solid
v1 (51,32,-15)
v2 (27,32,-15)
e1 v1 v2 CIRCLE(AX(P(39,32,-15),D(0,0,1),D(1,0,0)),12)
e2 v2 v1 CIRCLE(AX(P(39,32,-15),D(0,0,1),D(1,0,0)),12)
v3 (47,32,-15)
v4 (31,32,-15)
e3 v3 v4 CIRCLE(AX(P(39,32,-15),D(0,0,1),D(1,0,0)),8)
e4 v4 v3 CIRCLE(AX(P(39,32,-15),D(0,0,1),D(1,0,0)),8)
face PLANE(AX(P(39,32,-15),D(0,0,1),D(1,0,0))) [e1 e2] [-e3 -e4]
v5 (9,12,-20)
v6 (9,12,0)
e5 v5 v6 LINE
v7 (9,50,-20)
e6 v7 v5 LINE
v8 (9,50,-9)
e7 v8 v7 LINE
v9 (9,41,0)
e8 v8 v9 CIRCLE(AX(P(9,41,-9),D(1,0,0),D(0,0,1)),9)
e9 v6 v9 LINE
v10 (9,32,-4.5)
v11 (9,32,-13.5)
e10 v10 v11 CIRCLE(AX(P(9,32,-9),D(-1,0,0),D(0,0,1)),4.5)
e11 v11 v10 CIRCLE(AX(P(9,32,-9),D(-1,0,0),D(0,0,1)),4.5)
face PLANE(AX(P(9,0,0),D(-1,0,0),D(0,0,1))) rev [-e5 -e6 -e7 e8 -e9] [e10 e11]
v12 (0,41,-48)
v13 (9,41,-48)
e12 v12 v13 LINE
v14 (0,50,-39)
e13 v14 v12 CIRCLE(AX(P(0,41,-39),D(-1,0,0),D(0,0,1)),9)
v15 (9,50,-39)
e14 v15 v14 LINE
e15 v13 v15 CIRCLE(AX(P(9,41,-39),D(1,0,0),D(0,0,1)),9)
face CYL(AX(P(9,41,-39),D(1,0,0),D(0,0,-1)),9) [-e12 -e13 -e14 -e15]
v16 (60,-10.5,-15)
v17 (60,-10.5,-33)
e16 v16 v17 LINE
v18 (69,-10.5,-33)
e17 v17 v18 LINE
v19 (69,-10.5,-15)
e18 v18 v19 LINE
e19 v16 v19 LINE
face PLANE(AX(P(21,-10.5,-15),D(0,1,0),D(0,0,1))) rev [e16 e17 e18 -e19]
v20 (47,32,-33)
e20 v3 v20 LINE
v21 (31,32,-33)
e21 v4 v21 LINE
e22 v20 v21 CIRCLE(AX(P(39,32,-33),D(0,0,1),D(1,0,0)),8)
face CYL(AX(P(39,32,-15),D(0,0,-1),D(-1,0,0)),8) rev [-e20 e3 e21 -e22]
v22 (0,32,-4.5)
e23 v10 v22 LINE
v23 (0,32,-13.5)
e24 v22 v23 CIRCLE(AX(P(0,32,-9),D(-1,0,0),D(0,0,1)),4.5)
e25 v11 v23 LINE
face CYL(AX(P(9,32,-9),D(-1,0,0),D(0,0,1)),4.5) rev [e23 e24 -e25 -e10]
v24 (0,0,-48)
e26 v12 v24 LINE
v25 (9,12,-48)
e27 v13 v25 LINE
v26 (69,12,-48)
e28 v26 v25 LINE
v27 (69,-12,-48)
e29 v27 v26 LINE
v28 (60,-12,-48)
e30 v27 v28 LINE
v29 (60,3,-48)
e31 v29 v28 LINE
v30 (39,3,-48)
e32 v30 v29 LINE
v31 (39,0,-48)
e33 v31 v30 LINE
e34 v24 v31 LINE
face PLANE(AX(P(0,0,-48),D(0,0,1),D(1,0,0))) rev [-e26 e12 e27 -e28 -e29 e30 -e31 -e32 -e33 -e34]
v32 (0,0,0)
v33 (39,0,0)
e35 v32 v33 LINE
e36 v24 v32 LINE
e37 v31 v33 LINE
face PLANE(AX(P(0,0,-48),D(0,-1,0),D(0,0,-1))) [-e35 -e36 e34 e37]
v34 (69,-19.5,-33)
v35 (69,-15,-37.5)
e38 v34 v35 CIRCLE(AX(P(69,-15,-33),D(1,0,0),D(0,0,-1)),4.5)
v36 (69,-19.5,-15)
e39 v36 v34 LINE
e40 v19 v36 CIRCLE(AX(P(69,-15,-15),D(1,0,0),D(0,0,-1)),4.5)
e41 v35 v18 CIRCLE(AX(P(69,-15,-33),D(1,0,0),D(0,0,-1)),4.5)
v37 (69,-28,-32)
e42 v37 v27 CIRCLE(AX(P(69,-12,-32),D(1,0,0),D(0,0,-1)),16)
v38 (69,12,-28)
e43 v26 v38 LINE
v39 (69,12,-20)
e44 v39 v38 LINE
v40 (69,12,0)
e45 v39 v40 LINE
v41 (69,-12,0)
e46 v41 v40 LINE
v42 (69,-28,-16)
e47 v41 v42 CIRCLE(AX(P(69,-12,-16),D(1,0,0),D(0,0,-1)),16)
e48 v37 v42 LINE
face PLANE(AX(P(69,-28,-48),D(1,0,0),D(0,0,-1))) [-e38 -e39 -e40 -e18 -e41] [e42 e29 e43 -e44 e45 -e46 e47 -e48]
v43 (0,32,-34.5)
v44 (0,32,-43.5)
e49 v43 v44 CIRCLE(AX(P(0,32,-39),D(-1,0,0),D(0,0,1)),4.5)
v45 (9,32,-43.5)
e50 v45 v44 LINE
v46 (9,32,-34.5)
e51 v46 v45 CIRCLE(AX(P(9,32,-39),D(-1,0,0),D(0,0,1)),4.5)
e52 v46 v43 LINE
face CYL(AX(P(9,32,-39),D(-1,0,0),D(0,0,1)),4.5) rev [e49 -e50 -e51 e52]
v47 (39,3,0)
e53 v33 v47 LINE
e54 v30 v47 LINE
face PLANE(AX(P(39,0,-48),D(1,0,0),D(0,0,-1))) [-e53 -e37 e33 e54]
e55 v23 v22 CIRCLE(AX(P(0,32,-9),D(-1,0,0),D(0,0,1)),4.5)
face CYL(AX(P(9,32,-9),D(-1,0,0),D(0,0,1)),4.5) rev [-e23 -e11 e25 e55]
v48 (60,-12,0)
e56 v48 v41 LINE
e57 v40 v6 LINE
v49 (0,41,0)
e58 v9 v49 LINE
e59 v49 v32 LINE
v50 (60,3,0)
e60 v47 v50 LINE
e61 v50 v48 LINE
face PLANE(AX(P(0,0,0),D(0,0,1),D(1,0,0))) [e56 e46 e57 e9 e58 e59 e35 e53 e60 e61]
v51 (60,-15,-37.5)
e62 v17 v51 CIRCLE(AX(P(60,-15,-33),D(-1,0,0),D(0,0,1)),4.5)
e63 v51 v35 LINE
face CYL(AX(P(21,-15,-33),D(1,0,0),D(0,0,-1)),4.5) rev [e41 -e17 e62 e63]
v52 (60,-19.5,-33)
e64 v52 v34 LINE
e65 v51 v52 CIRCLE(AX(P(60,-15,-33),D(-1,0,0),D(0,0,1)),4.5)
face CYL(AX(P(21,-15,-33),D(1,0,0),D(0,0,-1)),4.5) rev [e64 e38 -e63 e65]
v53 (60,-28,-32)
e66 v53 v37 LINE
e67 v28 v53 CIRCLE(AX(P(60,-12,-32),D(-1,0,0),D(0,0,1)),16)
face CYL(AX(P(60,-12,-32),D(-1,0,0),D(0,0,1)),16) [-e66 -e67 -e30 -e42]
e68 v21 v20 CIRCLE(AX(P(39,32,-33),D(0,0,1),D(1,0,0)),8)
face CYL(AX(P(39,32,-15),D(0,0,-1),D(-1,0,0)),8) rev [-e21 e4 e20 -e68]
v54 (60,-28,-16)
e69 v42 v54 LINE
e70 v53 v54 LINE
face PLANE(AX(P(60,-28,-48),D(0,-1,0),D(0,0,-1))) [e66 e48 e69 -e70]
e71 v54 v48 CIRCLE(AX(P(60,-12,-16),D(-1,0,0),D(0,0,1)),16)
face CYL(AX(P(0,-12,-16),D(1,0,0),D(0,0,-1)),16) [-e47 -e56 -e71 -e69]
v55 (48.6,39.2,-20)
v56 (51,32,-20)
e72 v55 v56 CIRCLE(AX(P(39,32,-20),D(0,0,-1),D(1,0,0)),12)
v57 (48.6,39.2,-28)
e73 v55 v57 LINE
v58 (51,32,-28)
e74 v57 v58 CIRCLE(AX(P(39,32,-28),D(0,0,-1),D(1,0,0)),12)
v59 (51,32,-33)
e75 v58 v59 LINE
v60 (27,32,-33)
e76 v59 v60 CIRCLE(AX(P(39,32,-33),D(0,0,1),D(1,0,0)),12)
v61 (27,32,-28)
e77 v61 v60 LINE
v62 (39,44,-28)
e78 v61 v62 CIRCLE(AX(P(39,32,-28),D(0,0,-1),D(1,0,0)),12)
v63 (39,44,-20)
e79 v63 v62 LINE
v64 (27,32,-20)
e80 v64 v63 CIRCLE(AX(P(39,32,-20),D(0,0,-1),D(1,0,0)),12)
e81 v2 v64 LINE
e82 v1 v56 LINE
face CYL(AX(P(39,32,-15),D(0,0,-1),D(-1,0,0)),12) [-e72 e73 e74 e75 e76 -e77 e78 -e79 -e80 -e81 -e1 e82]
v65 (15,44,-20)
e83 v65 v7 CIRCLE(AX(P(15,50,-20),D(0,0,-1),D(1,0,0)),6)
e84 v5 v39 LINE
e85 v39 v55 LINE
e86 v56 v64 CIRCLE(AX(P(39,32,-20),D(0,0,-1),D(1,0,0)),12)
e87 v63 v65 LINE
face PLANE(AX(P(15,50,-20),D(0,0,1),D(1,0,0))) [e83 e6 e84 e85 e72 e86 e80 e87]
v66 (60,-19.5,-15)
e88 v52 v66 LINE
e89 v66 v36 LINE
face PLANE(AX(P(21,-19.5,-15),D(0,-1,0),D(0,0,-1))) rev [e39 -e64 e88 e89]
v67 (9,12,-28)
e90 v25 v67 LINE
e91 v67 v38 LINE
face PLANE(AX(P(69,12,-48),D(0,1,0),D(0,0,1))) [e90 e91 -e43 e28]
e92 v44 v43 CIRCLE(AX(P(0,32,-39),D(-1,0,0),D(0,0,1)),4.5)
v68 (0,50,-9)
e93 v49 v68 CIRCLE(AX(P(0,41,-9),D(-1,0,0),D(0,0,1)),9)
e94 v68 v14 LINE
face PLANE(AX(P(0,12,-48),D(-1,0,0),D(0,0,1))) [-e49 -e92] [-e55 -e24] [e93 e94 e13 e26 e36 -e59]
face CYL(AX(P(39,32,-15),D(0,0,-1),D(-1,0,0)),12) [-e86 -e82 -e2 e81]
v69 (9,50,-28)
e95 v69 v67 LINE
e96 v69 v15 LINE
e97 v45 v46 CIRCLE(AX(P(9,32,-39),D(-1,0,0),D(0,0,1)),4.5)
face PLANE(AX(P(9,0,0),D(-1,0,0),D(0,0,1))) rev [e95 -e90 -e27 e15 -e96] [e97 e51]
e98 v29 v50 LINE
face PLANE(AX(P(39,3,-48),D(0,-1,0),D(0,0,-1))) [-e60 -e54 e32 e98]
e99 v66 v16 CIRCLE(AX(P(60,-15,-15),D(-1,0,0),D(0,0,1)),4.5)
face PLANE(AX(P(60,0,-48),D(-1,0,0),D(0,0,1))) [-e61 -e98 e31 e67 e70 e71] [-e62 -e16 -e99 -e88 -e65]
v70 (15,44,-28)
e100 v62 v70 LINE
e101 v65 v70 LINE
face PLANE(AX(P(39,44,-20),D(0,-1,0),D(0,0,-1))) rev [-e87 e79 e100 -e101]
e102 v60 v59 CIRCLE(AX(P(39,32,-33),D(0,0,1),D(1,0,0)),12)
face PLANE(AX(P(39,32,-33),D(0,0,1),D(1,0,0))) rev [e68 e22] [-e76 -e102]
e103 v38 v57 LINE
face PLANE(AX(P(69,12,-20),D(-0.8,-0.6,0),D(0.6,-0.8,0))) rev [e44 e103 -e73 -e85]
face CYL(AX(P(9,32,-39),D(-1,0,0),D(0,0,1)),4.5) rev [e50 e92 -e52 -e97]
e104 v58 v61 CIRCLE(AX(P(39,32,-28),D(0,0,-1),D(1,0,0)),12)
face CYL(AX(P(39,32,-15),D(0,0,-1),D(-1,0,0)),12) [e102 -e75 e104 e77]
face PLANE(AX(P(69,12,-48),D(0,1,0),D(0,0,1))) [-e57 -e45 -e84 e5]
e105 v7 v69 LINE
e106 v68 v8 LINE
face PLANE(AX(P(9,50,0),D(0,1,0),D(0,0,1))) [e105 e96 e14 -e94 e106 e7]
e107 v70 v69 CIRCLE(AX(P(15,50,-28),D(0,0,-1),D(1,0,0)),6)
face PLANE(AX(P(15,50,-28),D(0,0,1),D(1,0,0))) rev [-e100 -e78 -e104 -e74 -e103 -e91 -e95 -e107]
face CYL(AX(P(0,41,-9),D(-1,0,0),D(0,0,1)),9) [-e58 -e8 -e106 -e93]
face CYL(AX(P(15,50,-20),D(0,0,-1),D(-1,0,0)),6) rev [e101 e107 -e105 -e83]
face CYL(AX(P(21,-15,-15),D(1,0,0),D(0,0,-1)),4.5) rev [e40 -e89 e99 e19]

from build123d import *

# Parameters (mm, degrees)
L_BRACKET_BASE_DEPTH                      = 48
BASE_CORNER_ROUNDS_R16_R                  = 16
SLOT_CUT_DEPTH                            = 48
BACK_PLATE_SKETCH_W                       = 48
BACK_PLATE_SKETCH_H                       = 38
BACK_PLATE_SKETCH_R                       = 4.5
BACK_PLATE_WITH_MOUNTING_HOLES_2X_9_DEPTH = 9
BEARING_HUB_SKETCH_R                      = 12
BEARING_HUB_SKETCH_R_2                    = 8
BEARING_HUB_DEPTH                         = 9
SUPPORT_RIB_DEPTH                         = 4
BEARING_BORE_SKETCH_R                     = 8
BEARING_BORE_16_DEPTH                     = 90.693923986
BACK_PLATE_CORNER_ROUNDS_R9_R             = 9


with BuildPart() as part:
    # L Bracket Profile Sketch → L Bracket Base (new body)
    with BuildSketch(Plane.XY):
        Polygon((0, 0), (39, 0), (39, 3), (60, 3), (60, 0), (60, -28), (69, -28), (69, 12), (0, 12), align=None)
    extrude(amount=-L_BRACKET_BASE_DEPTH)

    # Base Corner Rounds R16
    base_corner_rounds_r16_edges = [part.edges().sort_by_distance(p)[0] for p in [
        (64.5, -28, 0),
        (64.5, -28, -48),
    ]]
    fillet(base_corner_rounds_r16_edges, radius=BASE_CORNER_ROUNDS_R16_R)

    # Slot Sketch → Slot Cut (cut)
    with BuildSketch(Plane(origin=(69, 0, 0), x_dir=(0, 0, -1), z_dir=(1, 0, 0))):
        with BuildLine():
            Line((15, -10.5), (33, -10.5))
            ThreePointArc((33, -10.5), (37.5, -15), (33, -19.5))
            Line((33, -19.5), (15, -19.5))
            ThreePointArc((15, -19.5), (10.5, -15), (15, -10.5))
        make_face()
    extrude(amount=-SLOT_CUT_DEPTH, mode=Mode.SUBTRACT)

    # Back Plate Sketch → Back Plate with Mounting Holes 2xØ9 (add)
    with BuildSketch(Plane.ZY):
        with Locations((-24, 31)):
            Rectangle(BACK_PLATE_SKETCH_W, BACK_PLATE_SKETCH_H)
        with Locations((-39, 32)):
            Circle(BACK_PLATE_SKETCH_R, mode=Mode.SUBTRACT)
        with Locations((-9, 32)):
            Circle(BACK_PLATE_SKETCH_R, mode=Mode.SUBTRACT)
    extrude(amount=-BACK_PLATE_WITH_MOUNTING_HOLES_2X_9_DEPTH)



with BuildPart() as body_2:
    # Bearing Hub Sketch → Bearing Hub (new, symmetric)
    with BuildSketch(Plane.XY.offset(-24)):
        with Locations((39, 32)):
            Circle(BEARING_HUB_SKETCH_R)
        with Locations((39, 32)):
            Circle(BEARING_HUB_SKETCH_R_2, mode=Mode.SUBTRACT)
    extrude(amount=BEARING_HUB_DEPTH, both=True)


with BuildPart() as part_1:
    add(part.part)

    add(body_2.part)  # Support Rib merges body 2
    # Support Rib Sketch → Support Rib (add, symmetric)
    with BuildSketch(Plane.XY.offset(-24)):
        with BuildLine():
            Line((69, 12), (48.6, 39.2))
            ThreePointArc((48.6, 39.2), (44.276884864, 42.553769728), (39, 44))
            Line((39, 44), (15, 44))
            ThreePointArc((15, 44), (10.757359313, 45.757359313), (9, 50))
            Line((9, 50), (9, 12))
            Line((9, 12), (69, 12))
        make_face()
    extrude(amount=SUPPORT_RIB_DEPTH, both=True)

    # Bearing Bore Sketch → Bearing Bore Ø16 (cut, through all)
    with BuildSketch(Plane.XY.offset(-20)):
        with Locations((39, 32)):
            Circle(BEARING_BORE_SKETCH_R)
    extrude(amount=-BEARING_BORE_16_DEPTH, mode=Mode.SUBTRACT)

    # Back Plate Corner Rounds R9
    back_plate_corner_rounds_r9_edges = [part_1.edges().sort_by_distance(p)[0] for p in [
        (4.5, 50, -48),
        (4.5, 50, 0),
    ]]
    fillet(back_plate_corner_rounds_r9_edges, radius=BACK_PLATE_CORNER_ROUNDS_R9_R)


solid = part_1.part
